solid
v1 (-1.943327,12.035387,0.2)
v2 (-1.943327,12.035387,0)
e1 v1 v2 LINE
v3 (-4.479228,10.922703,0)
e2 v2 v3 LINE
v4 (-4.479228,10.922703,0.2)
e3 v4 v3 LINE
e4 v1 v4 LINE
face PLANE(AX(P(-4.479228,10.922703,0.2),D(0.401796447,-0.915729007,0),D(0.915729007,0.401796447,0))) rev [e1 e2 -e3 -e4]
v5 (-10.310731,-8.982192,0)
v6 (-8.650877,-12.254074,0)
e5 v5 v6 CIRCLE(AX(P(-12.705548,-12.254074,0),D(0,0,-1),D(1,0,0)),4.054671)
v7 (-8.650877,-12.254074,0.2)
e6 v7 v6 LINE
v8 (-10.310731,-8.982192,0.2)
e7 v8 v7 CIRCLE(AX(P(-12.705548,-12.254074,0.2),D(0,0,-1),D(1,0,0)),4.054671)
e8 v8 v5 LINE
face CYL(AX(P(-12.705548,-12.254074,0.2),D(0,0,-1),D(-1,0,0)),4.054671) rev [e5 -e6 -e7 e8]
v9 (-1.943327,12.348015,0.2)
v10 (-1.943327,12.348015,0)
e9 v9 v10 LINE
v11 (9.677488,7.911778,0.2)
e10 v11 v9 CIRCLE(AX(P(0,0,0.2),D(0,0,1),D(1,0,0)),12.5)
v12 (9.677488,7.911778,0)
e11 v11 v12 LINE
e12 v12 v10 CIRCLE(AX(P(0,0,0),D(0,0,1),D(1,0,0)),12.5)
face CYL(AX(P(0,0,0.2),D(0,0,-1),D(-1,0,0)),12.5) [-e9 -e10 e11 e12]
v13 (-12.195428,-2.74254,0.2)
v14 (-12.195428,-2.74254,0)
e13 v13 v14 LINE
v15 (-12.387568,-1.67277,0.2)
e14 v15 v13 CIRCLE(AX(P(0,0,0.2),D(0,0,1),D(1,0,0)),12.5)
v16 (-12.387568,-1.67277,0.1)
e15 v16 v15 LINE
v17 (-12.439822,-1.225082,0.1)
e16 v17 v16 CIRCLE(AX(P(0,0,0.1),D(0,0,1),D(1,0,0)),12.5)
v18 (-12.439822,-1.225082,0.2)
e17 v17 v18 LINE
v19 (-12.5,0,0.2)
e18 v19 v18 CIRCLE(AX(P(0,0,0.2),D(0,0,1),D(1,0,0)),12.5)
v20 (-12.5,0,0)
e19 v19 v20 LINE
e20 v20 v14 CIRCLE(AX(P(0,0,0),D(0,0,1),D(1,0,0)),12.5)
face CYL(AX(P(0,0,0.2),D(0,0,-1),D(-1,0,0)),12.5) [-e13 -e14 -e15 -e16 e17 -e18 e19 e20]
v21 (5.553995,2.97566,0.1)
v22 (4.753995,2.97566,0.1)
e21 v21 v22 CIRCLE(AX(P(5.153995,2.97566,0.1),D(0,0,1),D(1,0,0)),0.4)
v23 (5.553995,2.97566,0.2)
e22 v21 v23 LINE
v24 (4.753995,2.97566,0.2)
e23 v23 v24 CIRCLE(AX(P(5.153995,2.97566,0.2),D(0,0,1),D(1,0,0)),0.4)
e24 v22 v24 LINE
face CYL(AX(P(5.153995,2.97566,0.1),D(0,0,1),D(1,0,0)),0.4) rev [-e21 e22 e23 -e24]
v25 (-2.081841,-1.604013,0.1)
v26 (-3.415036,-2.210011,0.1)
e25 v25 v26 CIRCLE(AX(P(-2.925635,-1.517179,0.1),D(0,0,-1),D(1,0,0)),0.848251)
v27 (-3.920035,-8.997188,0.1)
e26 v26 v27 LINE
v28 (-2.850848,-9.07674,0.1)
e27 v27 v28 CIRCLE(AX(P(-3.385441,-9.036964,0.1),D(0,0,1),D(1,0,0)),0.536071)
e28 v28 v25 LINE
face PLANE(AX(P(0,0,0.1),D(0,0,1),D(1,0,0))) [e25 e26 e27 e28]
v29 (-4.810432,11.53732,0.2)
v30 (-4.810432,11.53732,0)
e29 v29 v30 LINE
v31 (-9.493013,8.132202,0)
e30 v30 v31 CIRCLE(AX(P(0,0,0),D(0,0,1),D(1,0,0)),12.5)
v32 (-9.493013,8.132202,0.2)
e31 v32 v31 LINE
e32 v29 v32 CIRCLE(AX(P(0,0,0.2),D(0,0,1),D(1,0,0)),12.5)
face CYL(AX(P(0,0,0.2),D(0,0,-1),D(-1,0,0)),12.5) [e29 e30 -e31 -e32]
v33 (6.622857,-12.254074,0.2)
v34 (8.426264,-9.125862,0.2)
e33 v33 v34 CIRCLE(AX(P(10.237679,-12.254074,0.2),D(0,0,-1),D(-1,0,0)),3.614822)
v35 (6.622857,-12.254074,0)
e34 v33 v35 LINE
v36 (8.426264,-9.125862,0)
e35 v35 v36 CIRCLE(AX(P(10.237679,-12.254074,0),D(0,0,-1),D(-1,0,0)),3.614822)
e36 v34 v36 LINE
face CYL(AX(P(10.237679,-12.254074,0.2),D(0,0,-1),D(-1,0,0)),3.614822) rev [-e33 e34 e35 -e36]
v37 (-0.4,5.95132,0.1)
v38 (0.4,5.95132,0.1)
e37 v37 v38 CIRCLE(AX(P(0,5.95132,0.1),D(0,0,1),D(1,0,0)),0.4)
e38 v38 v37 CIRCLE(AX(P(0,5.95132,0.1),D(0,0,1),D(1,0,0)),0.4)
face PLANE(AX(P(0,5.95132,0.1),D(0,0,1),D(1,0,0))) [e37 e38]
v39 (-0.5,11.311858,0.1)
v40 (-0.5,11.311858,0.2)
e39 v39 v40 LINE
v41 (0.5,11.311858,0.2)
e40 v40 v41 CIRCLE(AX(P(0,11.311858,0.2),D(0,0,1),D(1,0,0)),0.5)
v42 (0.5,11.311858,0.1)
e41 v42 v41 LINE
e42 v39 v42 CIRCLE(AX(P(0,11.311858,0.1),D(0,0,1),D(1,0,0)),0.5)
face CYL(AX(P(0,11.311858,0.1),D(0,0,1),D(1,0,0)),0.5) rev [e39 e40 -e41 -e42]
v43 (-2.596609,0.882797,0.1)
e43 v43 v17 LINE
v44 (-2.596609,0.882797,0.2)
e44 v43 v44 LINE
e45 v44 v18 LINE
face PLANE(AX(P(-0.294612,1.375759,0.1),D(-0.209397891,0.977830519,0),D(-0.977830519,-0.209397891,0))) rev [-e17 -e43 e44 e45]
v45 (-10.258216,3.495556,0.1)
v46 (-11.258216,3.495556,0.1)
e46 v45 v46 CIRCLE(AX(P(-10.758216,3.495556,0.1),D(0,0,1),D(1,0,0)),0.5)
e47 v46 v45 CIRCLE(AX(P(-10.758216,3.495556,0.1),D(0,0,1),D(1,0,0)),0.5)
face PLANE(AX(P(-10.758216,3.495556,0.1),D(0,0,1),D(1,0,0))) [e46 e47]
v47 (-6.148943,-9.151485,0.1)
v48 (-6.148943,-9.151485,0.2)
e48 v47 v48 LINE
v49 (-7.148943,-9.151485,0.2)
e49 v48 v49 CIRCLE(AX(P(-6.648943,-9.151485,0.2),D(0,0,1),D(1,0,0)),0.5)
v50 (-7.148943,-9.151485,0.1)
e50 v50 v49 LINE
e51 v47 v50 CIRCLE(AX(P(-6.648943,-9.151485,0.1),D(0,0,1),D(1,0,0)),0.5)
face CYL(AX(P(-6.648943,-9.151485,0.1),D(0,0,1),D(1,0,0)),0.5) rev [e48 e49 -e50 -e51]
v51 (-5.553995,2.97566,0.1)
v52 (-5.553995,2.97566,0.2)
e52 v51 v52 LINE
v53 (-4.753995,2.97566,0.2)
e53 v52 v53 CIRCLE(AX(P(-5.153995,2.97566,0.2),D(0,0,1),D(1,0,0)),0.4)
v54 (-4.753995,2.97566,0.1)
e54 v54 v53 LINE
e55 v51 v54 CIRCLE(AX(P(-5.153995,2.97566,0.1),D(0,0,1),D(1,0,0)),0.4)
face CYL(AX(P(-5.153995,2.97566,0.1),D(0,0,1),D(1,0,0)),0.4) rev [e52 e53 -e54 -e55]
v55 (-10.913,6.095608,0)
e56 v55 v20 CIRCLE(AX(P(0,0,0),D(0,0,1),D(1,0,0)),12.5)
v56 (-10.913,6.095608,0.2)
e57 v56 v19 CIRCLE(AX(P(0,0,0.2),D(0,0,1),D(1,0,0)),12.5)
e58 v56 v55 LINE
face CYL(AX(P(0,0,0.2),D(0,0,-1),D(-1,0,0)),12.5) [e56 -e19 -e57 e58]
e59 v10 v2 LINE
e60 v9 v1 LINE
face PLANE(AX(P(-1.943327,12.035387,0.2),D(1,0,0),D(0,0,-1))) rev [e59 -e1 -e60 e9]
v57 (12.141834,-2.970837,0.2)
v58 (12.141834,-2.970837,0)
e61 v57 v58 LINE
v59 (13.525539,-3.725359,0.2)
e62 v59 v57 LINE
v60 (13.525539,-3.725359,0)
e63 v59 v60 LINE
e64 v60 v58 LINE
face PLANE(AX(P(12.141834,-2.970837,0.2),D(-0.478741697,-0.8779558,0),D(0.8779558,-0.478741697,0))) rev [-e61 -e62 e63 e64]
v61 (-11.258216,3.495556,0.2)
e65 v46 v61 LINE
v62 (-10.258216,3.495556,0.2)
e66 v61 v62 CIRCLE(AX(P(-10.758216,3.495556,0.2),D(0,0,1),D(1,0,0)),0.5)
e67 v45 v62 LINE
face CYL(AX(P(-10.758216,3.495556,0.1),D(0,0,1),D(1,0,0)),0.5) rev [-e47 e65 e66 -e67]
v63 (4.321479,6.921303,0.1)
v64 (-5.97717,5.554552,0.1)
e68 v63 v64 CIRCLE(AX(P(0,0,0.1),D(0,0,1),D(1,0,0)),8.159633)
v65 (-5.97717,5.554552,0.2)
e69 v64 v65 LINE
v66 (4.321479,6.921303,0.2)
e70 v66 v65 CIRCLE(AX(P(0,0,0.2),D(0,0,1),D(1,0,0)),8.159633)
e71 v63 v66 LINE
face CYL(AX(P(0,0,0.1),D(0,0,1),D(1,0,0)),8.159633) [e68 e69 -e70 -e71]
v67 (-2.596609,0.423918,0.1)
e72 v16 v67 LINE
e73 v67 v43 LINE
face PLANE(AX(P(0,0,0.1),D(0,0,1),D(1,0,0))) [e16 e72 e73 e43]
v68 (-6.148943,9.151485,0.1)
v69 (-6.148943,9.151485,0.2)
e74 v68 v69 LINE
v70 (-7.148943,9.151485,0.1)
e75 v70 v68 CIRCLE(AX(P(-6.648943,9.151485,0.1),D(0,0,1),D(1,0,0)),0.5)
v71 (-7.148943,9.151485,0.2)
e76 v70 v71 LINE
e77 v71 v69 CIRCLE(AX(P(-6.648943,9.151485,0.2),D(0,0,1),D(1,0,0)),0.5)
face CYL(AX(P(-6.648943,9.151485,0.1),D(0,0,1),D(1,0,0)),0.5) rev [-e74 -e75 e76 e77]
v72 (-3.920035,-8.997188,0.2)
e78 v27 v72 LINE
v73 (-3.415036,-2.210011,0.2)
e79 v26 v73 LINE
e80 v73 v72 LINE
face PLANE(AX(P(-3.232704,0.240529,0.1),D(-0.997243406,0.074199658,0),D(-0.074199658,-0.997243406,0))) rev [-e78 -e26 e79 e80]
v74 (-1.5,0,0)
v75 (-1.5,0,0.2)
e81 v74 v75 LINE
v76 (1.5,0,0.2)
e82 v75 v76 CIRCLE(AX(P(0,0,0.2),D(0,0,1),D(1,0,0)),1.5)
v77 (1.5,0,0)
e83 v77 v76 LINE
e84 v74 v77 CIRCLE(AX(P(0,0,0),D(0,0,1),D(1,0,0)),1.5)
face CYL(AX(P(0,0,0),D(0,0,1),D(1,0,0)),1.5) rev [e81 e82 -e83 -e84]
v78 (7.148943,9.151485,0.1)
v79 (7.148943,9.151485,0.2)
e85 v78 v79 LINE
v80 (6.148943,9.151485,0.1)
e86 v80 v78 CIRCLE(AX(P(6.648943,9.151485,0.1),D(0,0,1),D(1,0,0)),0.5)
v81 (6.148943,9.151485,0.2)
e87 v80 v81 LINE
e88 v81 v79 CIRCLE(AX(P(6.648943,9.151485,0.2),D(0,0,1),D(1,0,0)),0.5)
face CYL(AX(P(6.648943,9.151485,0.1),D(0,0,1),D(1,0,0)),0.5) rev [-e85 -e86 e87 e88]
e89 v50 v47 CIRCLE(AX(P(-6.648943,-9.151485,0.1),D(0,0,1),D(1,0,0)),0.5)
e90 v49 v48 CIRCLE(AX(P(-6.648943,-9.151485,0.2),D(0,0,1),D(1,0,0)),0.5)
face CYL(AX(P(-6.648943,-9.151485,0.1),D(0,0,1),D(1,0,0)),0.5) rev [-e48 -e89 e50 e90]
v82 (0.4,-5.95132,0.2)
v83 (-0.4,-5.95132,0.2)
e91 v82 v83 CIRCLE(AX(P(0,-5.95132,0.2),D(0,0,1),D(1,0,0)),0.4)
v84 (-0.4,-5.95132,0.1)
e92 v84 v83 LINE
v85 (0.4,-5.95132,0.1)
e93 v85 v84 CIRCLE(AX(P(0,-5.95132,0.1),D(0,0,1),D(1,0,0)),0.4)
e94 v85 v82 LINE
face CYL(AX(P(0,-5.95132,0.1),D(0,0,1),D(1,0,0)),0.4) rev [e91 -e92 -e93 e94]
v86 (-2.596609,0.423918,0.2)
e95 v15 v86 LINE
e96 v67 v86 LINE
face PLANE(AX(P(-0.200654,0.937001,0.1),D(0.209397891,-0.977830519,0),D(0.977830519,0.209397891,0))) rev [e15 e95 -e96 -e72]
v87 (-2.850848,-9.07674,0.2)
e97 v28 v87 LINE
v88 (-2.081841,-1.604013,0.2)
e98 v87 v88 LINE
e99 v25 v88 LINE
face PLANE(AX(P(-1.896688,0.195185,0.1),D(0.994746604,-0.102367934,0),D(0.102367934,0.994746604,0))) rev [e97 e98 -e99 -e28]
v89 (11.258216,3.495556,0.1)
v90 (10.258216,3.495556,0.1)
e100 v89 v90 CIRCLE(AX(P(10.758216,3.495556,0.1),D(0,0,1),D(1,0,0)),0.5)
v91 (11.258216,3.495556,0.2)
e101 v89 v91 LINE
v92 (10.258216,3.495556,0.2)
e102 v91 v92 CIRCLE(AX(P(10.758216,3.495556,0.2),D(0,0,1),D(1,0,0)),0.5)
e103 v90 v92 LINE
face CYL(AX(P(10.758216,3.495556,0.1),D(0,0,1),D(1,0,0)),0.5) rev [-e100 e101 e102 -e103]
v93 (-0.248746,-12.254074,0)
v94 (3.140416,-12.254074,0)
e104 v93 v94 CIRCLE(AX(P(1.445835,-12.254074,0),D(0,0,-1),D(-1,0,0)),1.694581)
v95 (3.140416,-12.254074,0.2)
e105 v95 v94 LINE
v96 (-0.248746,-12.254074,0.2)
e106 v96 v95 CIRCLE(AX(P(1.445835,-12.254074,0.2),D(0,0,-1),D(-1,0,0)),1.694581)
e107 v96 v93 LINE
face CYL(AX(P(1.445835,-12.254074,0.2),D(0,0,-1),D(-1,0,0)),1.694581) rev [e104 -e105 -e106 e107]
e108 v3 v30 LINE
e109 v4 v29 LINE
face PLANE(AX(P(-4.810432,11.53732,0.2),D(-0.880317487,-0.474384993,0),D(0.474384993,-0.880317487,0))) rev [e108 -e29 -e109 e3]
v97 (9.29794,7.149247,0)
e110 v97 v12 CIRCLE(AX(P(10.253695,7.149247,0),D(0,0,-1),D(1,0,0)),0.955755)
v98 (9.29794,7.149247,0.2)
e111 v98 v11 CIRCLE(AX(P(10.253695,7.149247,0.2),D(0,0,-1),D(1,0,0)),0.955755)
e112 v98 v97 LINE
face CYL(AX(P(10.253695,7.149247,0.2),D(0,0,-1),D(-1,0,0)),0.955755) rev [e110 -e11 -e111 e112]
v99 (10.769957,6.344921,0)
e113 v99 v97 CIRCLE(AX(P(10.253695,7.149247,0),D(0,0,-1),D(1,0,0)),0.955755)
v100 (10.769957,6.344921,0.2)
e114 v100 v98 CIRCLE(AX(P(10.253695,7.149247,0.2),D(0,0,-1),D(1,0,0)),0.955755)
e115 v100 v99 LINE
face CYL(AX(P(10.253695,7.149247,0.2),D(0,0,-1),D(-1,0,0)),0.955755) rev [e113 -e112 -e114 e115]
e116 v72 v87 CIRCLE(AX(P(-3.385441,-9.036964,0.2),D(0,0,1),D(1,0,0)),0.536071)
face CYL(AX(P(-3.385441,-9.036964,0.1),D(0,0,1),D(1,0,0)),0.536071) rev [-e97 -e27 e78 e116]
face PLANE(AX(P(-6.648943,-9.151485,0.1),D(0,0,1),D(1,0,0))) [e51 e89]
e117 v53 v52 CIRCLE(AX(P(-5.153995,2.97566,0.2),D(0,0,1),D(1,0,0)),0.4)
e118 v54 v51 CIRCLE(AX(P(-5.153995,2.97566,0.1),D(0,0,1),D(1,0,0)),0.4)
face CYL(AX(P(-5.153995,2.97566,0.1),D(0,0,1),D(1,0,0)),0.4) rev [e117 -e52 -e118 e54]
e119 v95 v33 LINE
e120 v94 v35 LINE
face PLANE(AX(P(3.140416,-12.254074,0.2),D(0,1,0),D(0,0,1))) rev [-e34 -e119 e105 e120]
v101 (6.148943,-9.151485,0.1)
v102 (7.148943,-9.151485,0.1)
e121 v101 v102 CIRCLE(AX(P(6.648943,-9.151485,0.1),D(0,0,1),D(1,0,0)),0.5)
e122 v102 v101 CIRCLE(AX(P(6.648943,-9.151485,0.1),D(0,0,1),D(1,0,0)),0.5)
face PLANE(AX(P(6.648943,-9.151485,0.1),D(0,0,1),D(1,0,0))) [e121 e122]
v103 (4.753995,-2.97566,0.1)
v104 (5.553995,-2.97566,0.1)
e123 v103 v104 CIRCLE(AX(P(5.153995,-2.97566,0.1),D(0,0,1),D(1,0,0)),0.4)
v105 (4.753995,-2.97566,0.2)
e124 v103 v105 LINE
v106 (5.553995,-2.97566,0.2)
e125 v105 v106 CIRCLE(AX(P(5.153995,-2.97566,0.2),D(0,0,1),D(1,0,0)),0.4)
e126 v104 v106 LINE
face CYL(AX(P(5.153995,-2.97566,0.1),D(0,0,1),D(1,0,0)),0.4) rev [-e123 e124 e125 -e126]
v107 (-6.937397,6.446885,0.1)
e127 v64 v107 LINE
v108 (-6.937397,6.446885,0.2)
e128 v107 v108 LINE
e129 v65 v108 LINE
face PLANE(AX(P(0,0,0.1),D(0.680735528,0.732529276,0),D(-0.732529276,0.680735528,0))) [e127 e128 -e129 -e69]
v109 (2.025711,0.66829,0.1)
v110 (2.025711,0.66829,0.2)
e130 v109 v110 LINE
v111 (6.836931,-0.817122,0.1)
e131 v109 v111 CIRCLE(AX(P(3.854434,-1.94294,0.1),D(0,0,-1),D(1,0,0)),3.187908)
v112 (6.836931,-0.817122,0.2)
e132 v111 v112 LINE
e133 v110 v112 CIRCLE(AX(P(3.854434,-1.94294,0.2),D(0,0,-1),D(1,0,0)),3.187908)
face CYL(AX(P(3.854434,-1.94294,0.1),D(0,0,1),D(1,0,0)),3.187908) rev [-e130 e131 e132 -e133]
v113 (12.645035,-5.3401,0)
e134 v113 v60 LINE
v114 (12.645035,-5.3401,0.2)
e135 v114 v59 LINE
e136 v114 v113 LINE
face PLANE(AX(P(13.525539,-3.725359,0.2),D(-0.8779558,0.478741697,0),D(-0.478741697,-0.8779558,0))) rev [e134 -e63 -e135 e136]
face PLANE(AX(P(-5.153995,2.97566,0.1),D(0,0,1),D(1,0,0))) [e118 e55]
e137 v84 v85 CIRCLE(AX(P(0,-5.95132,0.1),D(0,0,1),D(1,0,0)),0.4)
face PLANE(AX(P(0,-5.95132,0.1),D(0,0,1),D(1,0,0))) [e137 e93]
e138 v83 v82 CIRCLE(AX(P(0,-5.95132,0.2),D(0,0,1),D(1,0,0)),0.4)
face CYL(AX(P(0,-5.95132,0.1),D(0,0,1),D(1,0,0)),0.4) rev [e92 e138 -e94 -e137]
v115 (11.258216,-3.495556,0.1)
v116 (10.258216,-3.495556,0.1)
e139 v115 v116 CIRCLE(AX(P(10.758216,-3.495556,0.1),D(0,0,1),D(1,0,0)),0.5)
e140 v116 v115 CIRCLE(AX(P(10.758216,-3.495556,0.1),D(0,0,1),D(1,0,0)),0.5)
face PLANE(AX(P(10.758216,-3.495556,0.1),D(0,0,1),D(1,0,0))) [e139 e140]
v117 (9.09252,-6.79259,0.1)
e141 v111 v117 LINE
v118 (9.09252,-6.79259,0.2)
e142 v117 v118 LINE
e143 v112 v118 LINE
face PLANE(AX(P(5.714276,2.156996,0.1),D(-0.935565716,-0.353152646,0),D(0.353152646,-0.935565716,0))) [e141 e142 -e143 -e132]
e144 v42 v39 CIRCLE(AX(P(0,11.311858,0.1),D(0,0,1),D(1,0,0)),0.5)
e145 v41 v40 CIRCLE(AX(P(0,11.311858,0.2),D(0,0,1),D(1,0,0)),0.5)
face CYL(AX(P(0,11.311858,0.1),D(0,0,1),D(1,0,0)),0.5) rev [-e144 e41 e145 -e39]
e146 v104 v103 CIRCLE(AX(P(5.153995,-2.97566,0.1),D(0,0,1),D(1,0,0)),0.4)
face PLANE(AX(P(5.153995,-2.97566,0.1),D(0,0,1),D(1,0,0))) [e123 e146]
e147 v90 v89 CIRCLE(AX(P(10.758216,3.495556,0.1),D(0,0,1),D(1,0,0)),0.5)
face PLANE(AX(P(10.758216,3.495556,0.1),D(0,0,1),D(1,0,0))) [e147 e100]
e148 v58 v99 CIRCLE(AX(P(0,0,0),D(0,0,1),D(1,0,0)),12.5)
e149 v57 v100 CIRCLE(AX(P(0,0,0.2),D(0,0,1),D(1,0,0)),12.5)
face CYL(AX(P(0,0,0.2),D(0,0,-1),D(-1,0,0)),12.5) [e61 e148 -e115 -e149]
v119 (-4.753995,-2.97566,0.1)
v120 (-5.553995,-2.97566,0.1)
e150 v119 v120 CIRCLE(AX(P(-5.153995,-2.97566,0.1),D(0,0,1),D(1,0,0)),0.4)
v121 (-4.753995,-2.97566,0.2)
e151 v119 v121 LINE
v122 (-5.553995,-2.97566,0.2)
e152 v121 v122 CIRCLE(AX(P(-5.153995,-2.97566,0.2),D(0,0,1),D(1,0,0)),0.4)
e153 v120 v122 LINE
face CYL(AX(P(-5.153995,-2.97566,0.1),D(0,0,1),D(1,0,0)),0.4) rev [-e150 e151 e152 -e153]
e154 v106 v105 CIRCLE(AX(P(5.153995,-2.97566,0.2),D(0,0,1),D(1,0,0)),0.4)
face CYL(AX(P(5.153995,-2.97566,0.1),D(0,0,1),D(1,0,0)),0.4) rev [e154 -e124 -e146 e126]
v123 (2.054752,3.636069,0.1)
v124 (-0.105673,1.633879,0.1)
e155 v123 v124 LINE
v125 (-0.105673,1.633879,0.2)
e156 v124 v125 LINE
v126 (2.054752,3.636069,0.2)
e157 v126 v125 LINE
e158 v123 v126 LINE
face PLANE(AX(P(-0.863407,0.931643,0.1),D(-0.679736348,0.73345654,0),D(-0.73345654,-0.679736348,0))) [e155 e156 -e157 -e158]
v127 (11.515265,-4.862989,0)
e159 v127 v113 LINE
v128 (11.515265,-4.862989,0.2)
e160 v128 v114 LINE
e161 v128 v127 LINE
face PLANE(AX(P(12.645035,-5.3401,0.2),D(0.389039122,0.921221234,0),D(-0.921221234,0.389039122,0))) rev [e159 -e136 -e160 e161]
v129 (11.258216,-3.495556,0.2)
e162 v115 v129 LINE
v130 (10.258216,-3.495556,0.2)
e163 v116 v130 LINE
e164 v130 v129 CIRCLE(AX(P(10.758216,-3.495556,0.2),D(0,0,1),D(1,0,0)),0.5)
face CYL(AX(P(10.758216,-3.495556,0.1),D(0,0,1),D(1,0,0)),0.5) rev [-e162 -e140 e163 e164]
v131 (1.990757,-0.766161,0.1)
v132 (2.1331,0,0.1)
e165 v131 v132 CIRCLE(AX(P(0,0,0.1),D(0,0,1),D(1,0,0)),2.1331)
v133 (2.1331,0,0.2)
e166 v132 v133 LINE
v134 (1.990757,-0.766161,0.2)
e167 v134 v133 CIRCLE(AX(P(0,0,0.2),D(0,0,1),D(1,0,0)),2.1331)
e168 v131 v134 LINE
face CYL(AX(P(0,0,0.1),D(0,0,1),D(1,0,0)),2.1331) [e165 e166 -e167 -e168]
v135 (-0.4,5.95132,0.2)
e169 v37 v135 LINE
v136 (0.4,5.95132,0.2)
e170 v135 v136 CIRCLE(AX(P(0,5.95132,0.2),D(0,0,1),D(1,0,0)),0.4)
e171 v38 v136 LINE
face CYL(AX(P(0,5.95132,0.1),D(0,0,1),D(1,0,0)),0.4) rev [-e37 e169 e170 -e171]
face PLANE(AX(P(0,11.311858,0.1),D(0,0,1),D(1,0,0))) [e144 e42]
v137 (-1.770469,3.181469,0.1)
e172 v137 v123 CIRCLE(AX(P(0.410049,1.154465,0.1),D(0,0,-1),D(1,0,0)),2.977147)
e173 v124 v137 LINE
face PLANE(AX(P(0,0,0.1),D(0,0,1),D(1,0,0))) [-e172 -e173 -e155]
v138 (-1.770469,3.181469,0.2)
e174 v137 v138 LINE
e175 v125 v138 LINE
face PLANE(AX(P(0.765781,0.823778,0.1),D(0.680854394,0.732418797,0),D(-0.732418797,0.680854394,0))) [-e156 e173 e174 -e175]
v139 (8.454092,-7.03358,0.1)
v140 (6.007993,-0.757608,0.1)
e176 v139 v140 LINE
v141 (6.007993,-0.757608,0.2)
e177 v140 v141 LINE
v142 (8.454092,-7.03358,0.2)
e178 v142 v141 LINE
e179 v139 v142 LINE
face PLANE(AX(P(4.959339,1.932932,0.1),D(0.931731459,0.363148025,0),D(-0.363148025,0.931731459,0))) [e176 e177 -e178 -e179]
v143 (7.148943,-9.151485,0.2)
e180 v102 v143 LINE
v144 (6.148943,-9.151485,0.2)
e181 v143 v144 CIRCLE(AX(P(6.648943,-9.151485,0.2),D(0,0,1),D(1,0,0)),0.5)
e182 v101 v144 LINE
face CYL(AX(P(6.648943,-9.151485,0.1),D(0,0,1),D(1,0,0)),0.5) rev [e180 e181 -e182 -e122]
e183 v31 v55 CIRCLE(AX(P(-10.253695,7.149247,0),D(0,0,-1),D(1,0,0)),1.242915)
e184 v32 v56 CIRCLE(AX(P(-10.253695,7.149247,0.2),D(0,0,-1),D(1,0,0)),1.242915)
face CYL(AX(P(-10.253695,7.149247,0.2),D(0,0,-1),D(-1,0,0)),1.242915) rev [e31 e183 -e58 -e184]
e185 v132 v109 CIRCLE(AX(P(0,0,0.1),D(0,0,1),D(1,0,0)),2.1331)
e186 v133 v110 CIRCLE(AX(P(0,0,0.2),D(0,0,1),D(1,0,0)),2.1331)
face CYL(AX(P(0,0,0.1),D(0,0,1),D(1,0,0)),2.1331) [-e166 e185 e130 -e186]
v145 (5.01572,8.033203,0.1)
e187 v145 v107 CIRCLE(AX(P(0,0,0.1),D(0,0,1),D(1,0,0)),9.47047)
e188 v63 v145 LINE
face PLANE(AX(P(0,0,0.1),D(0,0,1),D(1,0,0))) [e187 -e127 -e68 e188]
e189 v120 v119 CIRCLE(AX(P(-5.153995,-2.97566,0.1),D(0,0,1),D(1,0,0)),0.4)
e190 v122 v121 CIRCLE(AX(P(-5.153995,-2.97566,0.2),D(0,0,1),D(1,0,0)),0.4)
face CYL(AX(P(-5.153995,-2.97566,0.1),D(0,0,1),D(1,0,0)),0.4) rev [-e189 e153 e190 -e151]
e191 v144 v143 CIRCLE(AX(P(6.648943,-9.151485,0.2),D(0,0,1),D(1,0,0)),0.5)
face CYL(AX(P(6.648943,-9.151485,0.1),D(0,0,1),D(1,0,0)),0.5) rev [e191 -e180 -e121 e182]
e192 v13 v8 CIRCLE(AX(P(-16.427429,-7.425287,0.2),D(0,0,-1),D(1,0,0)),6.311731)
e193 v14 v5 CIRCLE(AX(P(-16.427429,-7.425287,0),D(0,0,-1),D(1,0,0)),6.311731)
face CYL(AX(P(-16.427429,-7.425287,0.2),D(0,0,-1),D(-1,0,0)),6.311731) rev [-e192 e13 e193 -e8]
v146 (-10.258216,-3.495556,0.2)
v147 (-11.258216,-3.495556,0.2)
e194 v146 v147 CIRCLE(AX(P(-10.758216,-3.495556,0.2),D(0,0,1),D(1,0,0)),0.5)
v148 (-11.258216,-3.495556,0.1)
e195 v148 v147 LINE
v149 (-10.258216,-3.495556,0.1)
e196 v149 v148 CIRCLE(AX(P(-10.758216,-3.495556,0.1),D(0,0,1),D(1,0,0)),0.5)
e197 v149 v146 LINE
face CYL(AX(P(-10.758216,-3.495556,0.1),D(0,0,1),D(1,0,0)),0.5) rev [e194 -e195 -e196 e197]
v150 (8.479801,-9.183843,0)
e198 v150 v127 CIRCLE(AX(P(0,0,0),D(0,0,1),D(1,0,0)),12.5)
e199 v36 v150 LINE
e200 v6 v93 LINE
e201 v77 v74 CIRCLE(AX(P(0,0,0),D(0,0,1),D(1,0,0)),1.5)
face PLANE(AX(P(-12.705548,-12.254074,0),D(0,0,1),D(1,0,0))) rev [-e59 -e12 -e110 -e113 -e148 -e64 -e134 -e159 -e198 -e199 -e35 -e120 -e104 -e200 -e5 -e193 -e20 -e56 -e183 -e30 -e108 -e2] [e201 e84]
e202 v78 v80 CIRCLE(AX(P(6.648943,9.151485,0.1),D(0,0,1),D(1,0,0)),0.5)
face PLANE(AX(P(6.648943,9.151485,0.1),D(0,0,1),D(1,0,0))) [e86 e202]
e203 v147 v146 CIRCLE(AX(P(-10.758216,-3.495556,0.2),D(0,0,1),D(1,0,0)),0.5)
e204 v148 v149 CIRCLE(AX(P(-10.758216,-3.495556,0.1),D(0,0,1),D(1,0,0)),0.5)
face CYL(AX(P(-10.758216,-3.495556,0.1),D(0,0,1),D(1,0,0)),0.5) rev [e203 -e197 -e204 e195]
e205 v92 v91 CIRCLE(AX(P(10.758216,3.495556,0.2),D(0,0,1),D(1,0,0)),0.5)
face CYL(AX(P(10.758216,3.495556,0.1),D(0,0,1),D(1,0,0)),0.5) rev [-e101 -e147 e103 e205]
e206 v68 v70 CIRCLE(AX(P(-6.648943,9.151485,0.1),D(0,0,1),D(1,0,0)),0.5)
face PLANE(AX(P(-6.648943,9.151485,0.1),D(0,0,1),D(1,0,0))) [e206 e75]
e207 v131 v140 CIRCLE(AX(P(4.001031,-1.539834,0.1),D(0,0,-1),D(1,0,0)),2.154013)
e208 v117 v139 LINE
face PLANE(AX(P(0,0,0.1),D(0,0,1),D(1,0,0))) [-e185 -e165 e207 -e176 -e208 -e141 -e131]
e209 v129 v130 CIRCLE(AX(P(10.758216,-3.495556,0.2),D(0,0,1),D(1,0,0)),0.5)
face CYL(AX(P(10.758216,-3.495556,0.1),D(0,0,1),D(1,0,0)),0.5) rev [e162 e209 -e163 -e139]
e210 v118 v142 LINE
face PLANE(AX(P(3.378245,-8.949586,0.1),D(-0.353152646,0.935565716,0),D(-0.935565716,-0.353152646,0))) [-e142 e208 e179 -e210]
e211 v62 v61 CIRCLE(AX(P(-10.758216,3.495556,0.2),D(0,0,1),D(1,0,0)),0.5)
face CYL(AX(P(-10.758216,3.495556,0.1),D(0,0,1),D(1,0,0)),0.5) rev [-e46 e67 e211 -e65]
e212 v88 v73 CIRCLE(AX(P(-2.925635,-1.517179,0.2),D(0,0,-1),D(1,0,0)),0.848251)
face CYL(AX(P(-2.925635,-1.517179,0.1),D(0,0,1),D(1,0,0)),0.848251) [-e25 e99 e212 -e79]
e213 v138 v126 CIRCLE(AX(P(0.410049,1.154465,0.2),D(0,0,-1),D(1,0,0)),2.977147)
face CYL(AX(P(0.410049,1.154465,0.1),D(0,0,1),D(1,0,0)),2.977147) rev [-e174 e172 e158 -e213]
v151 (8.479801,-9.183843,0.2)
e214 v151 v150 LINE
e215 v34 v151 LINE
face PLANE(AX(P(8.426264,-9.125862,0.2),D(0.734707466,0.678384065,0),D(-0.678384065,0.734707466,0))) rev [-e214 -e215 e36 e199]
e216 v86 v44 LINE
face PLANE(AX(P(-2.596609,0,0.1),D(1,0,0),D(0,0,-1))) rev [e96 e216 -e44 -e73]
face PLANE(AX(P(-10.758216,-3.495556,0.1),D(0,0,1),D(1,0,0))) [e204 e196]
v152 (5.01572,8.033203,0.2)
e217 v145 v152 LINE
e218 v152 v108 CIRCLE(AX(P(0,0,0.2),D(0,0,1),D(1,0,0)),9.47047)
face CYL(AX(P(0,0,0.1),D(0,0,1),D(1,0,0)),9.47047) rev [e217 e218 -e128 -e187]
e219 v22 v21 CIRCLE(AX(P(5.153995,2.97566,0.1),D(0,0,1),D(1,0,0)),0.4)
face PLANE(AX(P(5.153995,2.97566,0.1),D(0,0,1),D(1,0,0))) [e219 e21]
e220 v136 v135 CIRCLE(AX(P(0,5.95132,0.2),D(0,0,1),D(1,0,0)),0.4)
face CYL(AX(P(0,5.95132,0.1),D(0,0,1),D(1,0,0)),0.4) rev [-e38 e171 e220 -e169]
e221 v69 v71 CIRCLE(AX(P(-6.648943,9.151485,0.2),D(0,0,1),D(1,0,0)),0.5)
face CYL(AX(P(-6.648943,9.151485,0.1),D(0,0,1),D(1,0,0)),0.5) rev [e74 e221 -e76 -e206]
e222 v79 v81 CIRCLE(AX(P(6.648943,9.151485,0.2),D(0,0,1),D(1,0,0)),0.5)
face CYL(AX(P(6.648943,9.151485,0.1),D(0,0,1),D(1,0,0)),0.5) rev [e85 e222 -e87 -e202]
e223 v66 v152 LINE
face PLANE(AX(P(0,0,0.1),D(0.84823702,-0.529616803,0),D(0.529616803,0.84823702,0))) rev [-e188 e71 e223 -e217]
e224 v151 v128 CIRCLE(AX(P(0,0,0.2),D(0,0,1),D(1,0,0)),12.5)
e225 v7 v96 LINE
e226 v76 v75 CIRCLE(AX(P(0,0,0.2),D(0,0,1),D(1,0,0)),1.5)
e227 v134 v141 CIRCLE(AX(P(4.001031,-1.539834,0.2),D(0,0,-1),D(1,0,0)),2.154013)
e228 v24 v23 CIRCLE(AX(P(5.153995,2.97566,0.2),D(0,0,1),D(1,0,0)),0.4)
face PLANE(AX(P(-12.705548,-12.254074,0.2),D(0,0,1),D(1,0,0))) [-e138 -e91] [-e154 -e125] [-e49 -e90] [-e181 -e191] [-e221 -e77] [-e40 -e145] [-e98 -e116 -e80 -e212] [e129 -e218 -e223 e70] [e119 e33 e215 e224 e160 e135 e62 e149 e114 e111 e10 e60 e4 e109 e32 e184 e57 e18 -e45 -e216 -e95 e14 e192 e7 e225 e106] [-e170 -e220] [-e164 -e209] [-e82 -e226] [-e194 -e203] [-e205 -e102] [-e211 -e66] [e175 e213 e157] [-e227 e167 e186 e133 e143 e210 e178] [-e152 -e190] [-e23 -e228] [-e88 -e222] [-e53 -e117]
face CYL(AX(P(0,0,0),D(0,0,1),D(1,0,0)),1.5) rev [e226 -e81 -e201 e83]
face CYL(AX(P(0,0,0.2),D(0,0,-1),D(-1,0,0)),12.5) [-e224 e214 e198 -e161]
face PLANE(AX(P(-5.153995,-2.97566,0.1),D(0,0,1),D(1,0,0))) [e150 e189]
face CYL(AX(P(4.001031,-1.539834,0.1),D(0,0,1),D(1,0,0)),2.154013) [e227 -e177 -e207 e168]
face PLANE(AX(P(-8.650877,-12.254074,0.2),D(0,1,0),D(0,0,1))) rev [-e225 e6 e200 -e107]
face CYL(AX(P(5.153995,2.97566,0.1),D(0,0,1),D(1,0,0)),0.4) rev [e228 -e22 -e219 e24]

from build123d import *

# Parameters (mm, degrees)
BOSS_EXTRUDE2_DEPTH = 0.2
SKETCH4_R           = 1.5
CUT_EXTRUDE1_DEPTH  = 0.2
SKETCH5_R           = 0.5
CUT_EXTRUDE2_DEPTH  = 0.1
SKETCH6_R           = 0.4
CUT_EXTRUDE3_DEPTH  = 0.1
CUT_EXTRUDE6_DEPTH  = 0.1


with BuildPart() as part:
    # Sketch3 → Boss-Extrude2 (new body)
    with BuildSketch(Plane.XY):
        with BuildLine():
            Line((-8.650876673, -12.25407413), (-0.248745803, -12.25407413))
            ThreePointArc((-0.248745803, -12.25407413), (1.445834978, -10.55949335), (3.140415758, -12.25407413))
            Line((3.140415758, -12.25407413), (6.622856994, -12.25407413))
            ThreePointArc((6.622856994, -12.25407413), (7.105995692, -10.448666248), (8.426264063, -9.125861633))
            Line((8.426264063, -9.125861633), (8.479800816, -9.183843319))
            ThreePointArc((8.479800816, -9.183843319), (10.228299659, -7.185533111), (11.515265421, -4.862989028))
            Line((11.515265421, -4.862989028), (12.645034643, -5.340099639))
            Line((12.645034643, -5.340099639), (13.525538654, -3.725359149))
            Line((13.525538654, -3.725359149), (12.14183381, -2.970836876))
            ThreePointArc((12.14183381, -2.970836876), (12.366623578, 1.821159325), (10.769957457, 6.344920517))
            ThreePointArc((10.769957457, 6.344920517), (9.469693231, 6.602612743), (9.677487695, 7.91177805))
            ThreePointArc((9.677487695, 7.91177805), (4.458067099, 11.67799802), (-1.943326583, 12.348015298))
            Line((-1.943326583, 12.348015298), (-1.943326583, 12.035386554))
            Line((-1.943326583, 12.035386554), (-4.479228025, 10.922703455))
            Line((-4.479228025, 10.922703455), (-4.810432032, 11.537319605))
            ThreePointArc((-4.810432032, 11.537319605), (-7.351587465, 10.109607398), (-9.493012594, 8.132202155))
            ThreePointArc((-9.493012594, 8.132202155), (-9.234137218, 6.438374568), (-10.912999752, 6.095607961))
            ThreePointArc((-10.912999752, 6.095607961), (-12.370451822, 1.794971228), (-12.195428383, -2.742540164))
            ThreePointArc((-12.195428383, -2.742540164), (-10.385309853, -5.600254803), (-10.310731268, -8.98219213))
            ThreePointArc((-10.310731268, -8.98219213), (-9.089572731, -10.419658072), (-8.650876673, -12.25407413))
        make_face()
    extrude(amount=BOSS_EXTRUDE2_DEPTH)

    # Sketch4 → Cut-Extrude1 (cut)
    with BuildSketch(Plane.XY.offset(0.2)):
        Circle(SKETCH4_R)
    extrude(amount=-CUT_EXTRUDE1_DEPTH, mode=Mode.SUBTRACT)

    # Sketch5 → Cut-Extrude2 (cut)
    with BuildSketch(Plane.XY.offset(0.2)):
        with Locations((0, 11.311857504)):
            Circle(SKETCH5_R)
        with Locations((6.648943017, 9.151484959)):
            Circle(SKETCH5_R)
        with Locations((10.75821579, 3.495556207)):
            Circle(SKETCH5_R)
        with Locations((10.75821579, -3.495556207)):
            Circle(SKETCH5_R)
        with Locations((6.648943017, -9.151484959)):
            Circle(SKETCH5_R)
        with Locations((-6.648943017, -9.151484959)):
            Circle(SKETCH5_R)
        with Locations((-10.75821579, -3.495556207)):
            Circle(SKETCH5_R)
        with Locations((-10.75821579, 3.495556207)):
            Circle(SKETCH5_R)
        with Locations((-6.648943017, 9.151484959)):
            Circle(SKETCH5_R)
    extrude(amount=-CUT_EXTRUDE2_DEPTH, mode=Mode.SUBTRACT)

    # Sketch6 → Cut-Extrude3 (cut)
    with BuildSketch(Plane.XY.offset(0.2)):
        with Locations((0, 5.951320454)):
            Circle(SKETCH6_R)
        with Locations((5.153994699, 2.975660227)):
            Circle(SKETCH6_R)
        with Locations((5.153994699, -2.975660227)):
            Circle(SKETCH6_R)
        with Locations((0, -5.951320454)):
            Circle(SKETCH6_R)
        with Locations((-5.153994699, -2.975660227)):
            Circle(SKETCH6_R)
        with Locations((-5.153994699, 2.975660227)):
            Circle(SKETCH6_R)
    extrude(amount=-CUT_EXTRUDE3_DEPTH, mode=Mode.SUBTRACT)

    # Sketch7 → Cut-Extrude6 (cut)
    with BuildSketch(Plane.XY.offset(0.2)):
        with BuildLine():
            Line((-6.937396584, 6.446885446), (-6.51899849, 6.058070341))
            ThreePointArc((-6.51899849, 6.058070341), (-1.17077586, 8.821952247), (4.713219322, 7.548716526))
            Line((4.713219322, 7.548716526), (5.01572008, 8.033203309))
            ThreePointArc((5.01572008, 8.033203309), (-1.245917829, 9.388157012), (-6.937396584, 6.446885446))
        make_face()
        with BuildLine():
            Line((-6.51899849, 6.058070341), (-5.97717014, 5.554552161))
            ThreePointArc((-5.97717014, 5.554552161), (-1.073466502, 8.088713263), (4.321478804, 6.921302879))
            Line((4.321478804, 6.921302879), (4.713219322, 7.548716526))
            ThreePointArc((4.713219322, 7.548716526), (-1.17077586, 8.821952247), (-6.51899849, 6.058070341))
        make_face()
        Polygon((-13.213392068, -1.849616731), (-2.596608573, 0.423918438), (-2.596608573, 0.882797096), (-13.213392068, -1.390738073), align=None)
        with BuildLine():
            Line((-2.850848357, -9.076740417), (-2.081840804, -1.604013127))
            ThreePointArc((-2.081840804, -1.604013127), (-2.574626592, -2.289398349), (-3.41503625, -2.210011057))
            Line((-3.41503625, -2.210011057), (-3.920034525, -8.997187875))
            ThreePointArc((-3.920034525, -8.997187875), (-3.425217712, -9.571557231), (-2.850848357, -9.076740417))
        make_face()
        with BuildLine():
            ThreePointArc((-1.770469413, 3.181469047), (0.058709144, 4.110808601), (2.054752369, 3.636069044))
            Line((2.054752369, 3.636069044), (-0.105672739, 1.633878875))
            Line((-0.105672739, 1.633878875), (-1.770469413, 3.181469047))
        make_face()
        with BuildLine():
            ThreePointArc((1.990756871, -0.766161232), (2.132467077, -0.05196268), (2.025710728, 0.668290355))
            ThreePointArc((2.025710728, 0.668290355), (4.794865348, 1.103096967), (6.836930945, -0.817122344))
            Line((6.836930945, -0.817122344), (9.092520301, -6.792589594))
            Line((9.092520301, -6.792589594), (8.454091655, -7.033580432))
            Line((8.454091655, -7.033580432), (6.007993214, -0.757608342))
            ThreePointArc((6.007993214, -0.757608342), (3.996445347, 0.614174349), (1.990756871, -0.766161232))
        make_face()
    extrude(amount=-CUT_EXTRUDE6_DEPTH, mode=Mode.SUBTRACT)


solid = part.part
